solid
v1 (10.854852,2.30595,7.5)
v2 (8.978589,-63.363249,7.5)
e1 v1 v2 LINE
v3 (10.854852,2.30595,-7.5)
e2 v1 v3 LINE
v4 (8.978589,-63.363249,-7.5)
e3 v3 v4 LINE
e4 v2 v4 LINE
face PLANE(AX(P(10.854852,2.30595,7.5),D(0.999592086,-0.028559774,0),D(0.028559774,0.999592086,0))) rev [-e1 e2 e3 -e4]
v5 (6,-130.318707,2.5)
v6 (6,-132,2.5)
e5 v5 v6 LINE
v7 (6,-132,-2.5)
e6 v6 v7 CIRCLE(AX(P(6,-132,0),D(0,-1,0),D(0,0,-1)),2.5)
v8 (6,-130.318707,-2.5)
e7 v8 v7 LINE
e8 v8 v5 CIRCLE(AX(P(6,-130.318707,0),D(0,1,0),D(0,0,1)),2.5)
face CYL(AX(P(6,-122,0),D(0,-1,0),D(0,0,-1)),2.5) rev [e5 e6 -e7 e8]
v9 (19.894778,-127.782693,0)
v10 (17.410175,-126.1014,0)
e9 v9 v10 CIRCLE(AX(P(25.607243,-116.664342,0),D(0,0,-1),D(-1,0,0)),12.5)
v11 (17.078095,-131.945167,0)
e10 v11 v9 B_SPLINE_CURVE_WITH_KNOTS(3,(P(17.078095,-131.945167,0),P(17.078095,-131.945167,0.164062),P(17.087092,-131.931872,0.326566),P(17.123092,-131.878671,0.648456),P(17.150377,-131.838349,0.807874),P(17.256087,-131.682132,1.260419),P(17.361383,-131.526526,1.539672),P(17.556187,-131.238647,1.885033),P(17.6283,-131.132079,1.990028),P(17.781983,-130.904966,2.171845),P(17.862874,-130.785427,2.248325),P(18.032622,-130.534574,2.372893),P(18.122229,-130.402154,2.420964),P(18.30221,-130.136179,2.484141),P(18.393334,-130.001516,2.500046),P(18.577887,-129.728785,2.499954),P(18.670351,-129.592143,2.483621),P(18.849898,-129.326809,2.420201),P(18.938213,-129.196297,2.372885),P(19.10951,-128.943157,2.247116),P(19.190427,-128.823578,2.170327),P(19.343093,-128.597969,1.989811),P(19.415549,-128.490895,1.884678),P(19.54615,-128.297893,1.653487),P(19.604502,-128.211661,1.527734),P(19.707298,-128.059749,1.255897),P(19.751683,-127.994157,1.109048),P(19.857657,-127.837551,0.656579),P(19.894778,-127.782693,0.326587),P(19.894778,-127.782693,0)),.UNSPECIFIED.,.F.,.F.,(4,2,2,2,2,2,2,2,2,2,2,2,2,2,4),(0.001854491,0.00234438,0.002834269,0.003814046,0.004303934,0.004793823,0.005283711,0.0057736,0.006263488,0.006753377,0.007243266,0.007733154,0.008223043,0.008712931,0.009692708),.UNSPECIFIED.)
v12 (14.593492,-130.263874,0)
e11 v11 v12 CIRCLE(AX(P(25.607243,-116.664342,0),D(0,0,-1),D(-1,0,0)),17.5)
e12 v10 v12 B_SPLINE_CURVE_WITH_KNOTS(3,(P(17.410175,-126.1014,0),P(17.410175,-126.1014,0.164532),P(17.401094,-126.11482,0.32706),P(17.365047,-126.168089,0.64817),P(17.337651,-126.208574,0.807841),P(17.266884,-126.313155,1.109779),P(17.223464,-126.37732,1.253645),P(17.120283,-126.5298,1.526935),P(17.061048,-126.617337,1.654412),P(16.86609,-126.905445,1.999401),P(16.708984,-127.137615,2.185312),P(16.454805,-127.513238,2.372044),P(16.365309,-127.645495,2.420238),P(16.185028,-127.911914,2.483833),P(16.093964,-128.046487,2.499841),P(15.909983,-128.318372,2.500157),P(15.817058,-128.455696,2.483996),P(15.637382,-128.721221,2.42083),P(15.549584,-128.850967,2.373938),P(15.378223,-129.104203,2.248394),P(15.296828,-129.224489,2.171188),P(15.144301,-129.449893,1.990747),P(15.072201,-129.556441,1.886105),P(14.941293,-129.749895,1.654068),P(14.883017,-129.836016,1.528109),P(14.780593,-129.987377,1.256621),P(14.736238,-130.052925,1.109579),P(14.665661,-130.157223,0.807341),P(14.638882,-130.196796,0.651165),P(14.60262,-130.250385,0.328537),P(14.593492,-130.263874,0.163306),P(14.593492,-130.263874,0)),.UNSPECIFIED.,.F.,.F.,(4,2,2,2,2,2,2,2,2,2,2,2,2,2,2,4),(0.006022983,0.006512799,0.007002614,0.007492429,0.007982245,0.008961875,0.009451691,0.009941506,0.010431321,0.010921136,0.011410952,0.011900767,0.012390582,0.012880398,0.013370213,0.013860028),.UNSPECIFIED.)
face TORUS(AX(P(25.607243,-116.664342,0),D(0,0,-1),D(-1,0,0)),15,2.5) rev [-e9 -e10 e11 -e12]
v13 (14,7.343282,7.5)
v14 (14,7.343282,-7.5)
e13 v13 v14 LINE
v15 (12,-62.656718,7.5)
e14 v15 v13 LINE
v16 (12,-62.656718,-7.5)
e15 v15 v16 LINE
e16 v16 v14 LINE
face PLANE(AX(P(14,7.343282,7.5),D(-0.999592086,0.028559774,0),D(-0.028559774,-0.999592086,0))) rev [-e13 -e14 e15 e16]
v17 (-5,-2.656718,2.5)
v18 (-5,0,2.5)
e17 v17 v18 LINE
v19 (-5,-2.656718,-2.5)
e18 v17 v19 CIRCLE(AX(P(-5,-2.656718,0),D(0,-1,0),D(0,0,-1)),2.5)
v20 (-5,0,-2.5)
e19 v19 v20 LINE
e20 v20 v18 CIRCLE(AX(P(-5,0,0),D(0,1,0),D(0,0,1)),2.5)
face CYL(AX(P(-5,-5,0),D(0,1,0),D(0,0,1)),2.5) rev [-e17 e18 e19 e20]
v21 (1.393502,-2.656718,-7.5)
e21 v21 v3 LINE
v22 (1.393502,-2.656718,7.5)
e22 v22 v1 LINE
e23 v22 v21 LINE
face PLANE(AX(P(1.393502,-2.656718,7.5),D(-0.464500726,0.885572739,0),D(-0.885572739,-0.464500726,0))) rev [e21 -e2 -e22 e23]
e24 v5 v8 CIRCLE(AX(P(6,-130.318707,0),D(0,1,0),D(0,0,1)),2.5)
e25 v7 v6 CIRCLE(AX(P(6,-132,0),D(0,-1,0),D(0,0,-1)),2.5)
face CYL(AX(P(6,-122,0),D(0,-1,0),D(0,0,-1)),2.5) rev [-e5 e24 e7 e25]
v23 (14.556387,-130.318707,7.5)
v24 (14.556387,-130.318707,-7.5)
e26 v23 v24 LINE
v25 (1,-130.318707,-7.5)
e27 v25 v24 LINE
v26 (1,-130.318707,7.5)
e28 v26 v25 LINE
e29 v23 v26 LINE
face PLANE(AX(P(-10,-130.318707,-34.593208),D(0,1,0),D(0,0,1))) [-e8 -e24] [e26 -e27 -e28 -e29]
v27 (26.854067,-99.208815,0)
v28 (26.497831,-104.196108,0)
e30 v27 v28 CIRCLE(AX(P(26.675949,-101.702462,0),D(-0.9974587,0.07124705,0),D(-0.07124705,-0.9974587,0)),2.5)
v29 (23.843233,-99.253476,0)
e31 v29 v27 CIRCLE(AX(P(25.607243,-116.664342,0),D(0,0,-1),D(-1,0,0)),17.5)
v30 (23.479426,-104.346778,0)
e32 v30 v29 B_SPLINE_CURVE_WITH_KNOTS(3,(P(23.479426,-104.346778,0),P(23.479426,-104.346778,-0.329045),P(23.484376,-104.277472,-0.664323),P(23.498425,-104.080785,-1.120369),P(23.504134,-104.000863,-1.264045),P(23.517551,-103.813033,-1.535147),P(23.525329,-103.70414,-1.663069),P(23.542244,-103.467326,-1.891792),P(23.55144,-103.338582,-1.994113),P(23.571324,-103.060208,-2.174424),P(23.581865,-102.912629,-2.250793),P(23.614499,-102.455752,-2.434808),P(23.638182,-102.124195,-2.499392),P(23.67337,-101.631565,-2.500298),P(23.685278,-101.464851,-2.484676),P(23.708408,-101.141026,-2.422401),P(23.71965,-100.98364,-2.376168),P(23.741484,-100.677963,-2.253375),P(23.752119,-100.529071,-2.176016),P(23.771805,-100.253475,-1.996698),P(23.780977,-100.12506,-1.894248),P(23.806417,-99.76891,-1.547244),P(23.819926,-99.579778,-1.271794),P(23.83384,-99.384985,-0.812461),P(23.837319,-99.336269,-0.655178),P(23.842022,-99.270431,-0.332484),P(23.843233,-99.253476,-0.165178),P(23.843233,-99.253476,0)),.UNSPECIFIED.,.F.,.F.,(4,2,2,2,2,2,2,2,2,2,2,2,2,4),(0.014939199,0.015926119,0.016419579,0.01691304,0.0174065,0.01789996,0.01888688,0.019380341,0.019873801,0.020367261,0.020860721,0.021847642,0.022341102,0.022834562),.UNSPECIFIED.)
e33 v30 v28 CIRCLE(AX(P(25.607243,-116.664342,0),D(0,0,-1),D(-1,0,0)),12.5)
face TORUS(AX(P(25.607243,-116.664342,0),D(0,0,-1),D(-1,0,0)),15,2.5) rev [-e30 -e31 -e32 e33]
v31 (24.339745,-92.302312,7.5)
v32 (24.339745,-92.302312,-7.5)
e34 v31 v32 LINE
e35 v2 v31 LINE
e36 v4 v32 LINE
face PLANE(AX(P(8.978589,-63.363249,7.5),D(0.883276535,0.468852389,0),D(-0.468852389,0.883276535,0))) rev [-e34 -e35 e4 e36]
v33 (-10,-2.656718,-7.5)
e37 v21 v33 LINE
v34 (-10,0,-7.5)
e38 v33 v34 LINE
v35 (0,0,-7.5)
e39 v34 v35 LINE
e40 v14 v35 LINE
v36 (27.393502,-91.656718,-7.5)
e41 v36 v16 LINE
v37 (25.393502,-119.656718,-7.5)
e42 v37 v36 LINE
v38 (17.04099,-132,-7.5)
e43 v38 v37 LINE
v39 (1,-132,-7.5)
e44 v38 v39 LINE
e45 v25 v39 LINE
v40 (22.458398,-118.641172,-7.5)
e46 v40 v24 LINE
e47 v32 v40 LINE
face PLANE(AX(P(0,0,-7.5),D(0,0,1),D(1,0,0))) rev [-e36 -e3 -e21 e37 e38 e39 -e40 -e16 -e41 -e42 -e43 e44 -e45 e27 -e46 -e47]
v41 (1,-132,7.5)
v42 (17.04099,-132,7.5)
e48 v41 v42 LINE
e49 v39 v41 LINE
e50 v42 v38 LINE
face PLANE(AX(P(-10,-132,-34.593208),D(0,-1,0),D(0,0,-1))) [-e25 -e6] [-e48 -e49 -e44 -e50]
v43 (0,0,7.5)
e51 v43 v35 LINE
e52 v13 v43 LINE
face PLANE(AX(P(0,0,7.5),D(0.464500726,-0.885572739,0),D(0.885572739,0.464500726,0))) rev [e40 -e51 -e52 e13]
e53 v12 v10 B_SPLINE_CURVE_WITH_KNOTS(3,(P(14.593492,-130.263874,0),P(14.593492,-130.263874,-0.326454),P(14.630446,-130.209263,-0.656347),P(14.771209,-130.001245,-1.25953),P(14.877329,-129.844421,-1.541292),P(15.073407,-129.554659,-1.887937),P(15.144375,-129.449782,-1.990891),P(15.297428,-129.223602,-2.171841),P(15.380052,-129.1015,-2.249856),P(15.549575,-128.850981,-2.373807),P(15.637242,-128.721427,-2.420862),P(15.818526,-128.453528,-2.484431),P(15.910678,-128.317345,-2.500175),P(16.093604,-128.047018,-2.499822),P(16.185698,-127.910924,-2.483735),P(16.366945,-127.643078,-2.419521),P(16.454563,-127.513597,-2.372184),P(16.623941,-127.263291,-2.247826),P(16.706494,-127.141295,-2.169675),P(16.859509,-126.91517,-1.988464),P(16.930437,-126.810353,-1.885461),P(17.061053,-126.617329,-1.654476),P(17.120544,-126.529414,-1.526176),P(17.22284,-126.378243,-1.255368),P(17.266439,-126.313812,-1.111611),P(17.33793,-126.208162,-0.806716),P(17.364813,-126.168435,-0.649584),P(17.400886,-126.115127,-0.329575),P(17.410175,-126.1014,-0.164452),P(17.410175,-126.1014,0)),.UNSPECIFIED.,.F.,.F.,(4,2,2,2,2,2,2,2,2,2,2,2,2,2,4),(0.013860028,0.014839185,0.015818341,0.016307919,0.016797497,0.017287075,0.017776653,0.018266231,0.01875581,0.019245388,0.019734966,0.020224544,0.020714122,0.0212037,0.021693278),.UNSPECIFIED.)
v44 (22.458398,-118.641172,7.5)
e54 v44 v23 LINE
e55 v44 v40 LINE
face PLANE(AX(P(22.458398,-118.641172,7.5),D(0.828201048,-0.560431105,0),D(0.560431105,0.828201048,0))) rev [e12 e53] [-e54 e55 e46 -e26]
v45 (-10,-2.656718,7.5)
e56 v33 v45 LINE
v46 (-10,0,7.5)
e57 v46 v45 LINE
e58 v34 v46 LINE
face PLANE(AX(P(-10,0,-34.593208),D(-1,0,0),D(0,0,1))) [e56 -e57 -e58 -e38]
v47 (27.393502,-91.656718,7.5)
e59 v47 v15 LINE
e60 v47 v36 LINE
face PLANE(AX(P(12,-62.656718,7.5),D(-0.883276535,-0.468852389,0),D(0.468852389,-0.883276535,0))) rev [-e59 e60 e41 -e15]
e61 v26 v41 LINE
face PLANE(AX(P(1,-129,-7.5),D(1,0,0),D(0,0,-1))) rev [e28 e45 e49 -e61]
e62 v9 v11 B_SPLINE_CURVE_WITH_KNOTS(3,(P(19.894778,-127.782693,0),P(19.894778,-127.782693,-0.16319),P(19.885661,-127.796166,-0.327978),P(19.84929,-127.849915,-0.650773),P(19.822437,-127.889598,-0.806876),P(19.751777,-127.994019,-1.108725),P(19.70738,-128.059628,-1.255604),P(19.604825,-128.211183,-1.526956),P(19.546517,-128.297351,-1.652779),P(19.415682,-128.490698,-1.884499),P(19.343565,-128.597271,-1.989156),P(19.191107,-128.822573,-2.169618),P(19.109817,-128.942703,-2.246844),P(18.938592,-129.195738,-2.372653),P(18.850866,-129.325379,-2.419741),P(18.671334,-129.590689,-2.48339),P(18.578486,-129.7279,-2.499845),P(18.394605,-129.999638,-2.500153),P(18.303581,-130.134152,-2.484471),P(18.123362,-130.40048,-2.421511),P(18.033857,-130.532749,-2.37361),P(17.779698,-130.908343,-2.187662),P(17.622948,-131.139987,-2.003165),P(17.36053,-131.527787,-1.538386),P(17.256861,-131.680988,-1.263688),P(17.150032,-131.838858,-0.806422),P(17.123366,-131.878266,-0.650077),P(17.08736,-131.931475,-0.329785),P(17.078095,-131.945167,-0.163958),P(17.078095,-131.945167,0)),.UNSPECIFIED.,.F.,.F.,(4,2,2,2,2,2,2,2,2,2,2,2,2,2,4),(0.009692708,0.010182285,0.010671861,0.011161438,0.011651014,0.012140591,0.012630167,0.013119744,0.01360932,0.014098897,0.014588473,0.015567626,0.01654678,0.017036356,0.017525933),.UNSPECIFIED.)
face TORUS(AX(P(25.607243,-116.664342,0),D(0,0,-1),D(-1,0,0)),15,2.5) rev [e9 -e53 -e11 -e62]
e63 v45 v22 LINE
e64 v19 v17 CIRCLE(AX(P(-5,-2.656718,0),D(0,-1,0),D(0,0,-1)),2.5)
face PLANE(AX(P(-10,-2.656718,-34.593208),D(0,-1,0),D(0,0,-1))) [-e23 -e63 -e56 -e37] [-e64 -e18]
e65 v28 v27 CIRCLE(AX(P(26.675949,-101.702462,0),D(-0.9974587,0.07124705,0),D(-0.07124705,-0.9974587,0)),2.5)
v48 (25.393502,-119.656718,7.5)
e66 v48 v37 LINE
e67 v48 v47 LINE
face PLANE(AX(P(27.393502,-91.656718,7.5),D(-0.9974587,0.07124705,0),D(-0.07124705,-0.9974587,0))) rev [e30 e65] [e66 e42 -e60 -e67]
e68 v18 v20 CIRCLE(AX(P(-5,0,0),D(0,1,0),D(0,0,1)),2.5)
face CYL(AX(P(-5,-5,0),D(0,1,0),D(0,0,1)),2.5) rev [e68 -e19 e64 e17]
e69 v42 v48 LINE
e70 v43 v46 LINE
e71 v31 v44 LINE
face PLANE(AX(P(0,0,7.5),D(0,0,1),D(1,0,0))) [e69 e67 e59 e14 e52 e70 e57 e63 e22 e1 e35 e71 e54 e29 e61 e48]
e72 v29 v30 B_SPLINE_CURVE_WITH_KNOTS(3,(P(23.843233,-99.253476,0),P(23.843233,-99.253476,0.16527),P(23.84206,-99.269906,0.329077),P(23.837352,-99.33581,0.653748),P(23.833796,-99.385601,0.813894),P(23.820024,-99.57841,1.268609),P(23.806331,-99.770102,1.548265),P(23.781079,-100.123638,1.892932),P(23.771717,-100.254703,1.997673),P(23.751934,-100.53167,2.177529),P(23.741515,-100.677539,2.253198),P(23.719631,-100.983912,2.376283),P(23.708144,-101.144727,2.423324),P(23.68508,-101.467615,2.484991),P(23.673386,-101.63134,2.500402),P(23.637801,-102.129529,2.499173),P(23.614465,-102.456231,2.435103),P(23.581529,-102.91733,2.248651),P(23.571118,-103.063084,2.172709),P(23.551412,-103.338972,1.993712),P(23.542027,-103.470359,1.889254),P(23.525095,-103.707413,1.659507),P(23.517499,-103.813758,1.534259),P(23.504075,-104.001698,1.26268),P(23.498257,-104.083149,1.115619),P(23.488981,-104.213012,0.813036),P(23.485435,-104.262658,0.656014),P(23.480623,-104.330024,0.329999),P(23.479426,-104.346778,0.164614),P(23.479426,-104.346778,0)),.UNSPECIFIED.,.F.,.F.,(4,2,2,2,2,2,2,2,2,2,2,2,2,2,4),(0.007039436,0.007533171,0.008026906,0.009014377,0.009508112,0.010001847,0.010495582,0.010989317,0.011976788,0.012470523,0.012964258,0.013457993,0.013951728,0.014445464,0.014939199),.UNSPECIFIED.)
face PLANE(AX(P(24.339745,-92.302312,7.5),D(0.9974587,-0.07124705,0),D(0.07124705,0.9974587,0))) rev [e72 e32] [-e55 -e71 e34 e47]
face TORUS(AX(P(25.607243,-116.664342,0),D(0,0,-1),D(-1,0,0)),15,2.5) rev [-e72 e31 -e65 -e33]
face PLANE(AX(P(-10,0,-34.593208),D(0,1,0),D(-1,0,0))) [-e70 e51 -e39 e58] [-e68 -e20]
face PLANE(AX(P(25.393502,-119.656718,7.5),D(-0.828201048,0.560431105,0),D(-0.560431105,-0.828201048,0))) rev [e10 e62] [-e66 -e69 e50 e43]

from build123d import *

# Parameters (mm, degrees)
EXTRUDE_1_DEPTH     = 7.5
SKETCH_2_W          = 11.393502177
SKETCH_2_H          = 2.656718216
SKETCH_2_W_2        = 27.04099035
SKETCH_2_H_2        = 1.681293315
EXTRUDE_2_DEPTH     = 15
SKETCH_3_R          = 2.5
CUT_EXTRUDE_1_DEPTH = 5
SKETCH_4_R          = 2.5
CUT_EXTRUDE_2_DEPTH = 10
SKETCH_5_W          = 11
SKETCH_5_H          = 15
CUT_EXTRUDE_3_DEPTH = 3
SKETCH_9_R          = 2.5


with BuildPart() as part:
    # 草图1 → 凸台-拉伸1 (new, symmetric)
    with BuildSketch(Plane.XY):
        Polygon((0, 0), (14, 7.343281784), (12, -62.656718216), (27.393502177, -91.656718216), (25.393502177, -119.656718216), (17.04099035, -132), (14.556387205, -130.318706685), (22.458397846, -118.641172307), (24.339745043, -92.302311555), (8.978589163, -63.363249125), (10.854852, 2.305950198), (1.393502177, -2.656718216), align=None)
    extrude(amount=EXTRUDE_1_DEPTH, both=True)

    # 草图2 → 凸台-拉伸2 (add)
    with BuildSketch(Plane.XY.offset(7.5)):
        with Locations((-4.303248911, -1.328359108)):
            Rectangle(SKETCH_2_W, SKETCH_2_H)
        with Locations((3.520495175, -131.159353342)):
            Rectangle(SKETCH_2_W_2, SKETCH_2_H_2)
    extrude(amount=-EXTRUDE_2_DEPTH)

    # 草图3 → 切除-拉伸1 (cut)
    with BuildSketch(Plane(origin=(0, 0, 0), x_dir=(1, 0, 0), z_dir=(0, 1, 0))):
        with Locations(Location((-5, 0, 0), (0, 0, 270))):
            Circle(SKETCH_3_R)
    extrude(amount=-CUT_EXTRUDE_1_DEPTH, mode=Mode.SUBTRACT)

    # 草图4 → 切除-拉伸2 (cut)
    with BuildSketch(Plane.XZ.offset(132)):
        with Locations(Location((6, 0, 0), (0, 0, 270))):
            Circle(SKETCH_4_R)
    extrude(amount=-CUT_EXTRUDE_2_DEPTH, mode=Mode.SUBTRACT)

    # 草图5 → 切除-拉伸3 (cut)
    with BuildSketch(Plane.XZ.offset(132)):
        with Locations((-4.5, 0)):
            Rectangle(SKETCH_5_W, SKETCH_5_H)
    extrude(amount=-CUT_EXTRUDE_3_DEPTH, mode=Mode.SUBTRACT)

    # 草图9 → 切除-旋转1 (revolve, cut)
    with BuildSketch(Plane(origin=(33.768124273, -2.412008877, 0), x_dir=(0, 0, -1), z_dir=(0.997458699830735, -0.07124704998790972, 0)), mode=Mode.PRIVATE) as cut_revolve_1_sk:
        with Locations((0, -99.543422459)):
            Circle(SKETCH_9_R)
    revolve(cut_revolve_1_sk.sketch.rotate(Axis((25.607243327, -116.664342117, 0), (0, 0, 1)), 6.860802101), axis=Axis((25.607243327, -116.664342117, 0), (0, 0, 1)), mode=Mode.SUBTRACT)


solid = part.part
